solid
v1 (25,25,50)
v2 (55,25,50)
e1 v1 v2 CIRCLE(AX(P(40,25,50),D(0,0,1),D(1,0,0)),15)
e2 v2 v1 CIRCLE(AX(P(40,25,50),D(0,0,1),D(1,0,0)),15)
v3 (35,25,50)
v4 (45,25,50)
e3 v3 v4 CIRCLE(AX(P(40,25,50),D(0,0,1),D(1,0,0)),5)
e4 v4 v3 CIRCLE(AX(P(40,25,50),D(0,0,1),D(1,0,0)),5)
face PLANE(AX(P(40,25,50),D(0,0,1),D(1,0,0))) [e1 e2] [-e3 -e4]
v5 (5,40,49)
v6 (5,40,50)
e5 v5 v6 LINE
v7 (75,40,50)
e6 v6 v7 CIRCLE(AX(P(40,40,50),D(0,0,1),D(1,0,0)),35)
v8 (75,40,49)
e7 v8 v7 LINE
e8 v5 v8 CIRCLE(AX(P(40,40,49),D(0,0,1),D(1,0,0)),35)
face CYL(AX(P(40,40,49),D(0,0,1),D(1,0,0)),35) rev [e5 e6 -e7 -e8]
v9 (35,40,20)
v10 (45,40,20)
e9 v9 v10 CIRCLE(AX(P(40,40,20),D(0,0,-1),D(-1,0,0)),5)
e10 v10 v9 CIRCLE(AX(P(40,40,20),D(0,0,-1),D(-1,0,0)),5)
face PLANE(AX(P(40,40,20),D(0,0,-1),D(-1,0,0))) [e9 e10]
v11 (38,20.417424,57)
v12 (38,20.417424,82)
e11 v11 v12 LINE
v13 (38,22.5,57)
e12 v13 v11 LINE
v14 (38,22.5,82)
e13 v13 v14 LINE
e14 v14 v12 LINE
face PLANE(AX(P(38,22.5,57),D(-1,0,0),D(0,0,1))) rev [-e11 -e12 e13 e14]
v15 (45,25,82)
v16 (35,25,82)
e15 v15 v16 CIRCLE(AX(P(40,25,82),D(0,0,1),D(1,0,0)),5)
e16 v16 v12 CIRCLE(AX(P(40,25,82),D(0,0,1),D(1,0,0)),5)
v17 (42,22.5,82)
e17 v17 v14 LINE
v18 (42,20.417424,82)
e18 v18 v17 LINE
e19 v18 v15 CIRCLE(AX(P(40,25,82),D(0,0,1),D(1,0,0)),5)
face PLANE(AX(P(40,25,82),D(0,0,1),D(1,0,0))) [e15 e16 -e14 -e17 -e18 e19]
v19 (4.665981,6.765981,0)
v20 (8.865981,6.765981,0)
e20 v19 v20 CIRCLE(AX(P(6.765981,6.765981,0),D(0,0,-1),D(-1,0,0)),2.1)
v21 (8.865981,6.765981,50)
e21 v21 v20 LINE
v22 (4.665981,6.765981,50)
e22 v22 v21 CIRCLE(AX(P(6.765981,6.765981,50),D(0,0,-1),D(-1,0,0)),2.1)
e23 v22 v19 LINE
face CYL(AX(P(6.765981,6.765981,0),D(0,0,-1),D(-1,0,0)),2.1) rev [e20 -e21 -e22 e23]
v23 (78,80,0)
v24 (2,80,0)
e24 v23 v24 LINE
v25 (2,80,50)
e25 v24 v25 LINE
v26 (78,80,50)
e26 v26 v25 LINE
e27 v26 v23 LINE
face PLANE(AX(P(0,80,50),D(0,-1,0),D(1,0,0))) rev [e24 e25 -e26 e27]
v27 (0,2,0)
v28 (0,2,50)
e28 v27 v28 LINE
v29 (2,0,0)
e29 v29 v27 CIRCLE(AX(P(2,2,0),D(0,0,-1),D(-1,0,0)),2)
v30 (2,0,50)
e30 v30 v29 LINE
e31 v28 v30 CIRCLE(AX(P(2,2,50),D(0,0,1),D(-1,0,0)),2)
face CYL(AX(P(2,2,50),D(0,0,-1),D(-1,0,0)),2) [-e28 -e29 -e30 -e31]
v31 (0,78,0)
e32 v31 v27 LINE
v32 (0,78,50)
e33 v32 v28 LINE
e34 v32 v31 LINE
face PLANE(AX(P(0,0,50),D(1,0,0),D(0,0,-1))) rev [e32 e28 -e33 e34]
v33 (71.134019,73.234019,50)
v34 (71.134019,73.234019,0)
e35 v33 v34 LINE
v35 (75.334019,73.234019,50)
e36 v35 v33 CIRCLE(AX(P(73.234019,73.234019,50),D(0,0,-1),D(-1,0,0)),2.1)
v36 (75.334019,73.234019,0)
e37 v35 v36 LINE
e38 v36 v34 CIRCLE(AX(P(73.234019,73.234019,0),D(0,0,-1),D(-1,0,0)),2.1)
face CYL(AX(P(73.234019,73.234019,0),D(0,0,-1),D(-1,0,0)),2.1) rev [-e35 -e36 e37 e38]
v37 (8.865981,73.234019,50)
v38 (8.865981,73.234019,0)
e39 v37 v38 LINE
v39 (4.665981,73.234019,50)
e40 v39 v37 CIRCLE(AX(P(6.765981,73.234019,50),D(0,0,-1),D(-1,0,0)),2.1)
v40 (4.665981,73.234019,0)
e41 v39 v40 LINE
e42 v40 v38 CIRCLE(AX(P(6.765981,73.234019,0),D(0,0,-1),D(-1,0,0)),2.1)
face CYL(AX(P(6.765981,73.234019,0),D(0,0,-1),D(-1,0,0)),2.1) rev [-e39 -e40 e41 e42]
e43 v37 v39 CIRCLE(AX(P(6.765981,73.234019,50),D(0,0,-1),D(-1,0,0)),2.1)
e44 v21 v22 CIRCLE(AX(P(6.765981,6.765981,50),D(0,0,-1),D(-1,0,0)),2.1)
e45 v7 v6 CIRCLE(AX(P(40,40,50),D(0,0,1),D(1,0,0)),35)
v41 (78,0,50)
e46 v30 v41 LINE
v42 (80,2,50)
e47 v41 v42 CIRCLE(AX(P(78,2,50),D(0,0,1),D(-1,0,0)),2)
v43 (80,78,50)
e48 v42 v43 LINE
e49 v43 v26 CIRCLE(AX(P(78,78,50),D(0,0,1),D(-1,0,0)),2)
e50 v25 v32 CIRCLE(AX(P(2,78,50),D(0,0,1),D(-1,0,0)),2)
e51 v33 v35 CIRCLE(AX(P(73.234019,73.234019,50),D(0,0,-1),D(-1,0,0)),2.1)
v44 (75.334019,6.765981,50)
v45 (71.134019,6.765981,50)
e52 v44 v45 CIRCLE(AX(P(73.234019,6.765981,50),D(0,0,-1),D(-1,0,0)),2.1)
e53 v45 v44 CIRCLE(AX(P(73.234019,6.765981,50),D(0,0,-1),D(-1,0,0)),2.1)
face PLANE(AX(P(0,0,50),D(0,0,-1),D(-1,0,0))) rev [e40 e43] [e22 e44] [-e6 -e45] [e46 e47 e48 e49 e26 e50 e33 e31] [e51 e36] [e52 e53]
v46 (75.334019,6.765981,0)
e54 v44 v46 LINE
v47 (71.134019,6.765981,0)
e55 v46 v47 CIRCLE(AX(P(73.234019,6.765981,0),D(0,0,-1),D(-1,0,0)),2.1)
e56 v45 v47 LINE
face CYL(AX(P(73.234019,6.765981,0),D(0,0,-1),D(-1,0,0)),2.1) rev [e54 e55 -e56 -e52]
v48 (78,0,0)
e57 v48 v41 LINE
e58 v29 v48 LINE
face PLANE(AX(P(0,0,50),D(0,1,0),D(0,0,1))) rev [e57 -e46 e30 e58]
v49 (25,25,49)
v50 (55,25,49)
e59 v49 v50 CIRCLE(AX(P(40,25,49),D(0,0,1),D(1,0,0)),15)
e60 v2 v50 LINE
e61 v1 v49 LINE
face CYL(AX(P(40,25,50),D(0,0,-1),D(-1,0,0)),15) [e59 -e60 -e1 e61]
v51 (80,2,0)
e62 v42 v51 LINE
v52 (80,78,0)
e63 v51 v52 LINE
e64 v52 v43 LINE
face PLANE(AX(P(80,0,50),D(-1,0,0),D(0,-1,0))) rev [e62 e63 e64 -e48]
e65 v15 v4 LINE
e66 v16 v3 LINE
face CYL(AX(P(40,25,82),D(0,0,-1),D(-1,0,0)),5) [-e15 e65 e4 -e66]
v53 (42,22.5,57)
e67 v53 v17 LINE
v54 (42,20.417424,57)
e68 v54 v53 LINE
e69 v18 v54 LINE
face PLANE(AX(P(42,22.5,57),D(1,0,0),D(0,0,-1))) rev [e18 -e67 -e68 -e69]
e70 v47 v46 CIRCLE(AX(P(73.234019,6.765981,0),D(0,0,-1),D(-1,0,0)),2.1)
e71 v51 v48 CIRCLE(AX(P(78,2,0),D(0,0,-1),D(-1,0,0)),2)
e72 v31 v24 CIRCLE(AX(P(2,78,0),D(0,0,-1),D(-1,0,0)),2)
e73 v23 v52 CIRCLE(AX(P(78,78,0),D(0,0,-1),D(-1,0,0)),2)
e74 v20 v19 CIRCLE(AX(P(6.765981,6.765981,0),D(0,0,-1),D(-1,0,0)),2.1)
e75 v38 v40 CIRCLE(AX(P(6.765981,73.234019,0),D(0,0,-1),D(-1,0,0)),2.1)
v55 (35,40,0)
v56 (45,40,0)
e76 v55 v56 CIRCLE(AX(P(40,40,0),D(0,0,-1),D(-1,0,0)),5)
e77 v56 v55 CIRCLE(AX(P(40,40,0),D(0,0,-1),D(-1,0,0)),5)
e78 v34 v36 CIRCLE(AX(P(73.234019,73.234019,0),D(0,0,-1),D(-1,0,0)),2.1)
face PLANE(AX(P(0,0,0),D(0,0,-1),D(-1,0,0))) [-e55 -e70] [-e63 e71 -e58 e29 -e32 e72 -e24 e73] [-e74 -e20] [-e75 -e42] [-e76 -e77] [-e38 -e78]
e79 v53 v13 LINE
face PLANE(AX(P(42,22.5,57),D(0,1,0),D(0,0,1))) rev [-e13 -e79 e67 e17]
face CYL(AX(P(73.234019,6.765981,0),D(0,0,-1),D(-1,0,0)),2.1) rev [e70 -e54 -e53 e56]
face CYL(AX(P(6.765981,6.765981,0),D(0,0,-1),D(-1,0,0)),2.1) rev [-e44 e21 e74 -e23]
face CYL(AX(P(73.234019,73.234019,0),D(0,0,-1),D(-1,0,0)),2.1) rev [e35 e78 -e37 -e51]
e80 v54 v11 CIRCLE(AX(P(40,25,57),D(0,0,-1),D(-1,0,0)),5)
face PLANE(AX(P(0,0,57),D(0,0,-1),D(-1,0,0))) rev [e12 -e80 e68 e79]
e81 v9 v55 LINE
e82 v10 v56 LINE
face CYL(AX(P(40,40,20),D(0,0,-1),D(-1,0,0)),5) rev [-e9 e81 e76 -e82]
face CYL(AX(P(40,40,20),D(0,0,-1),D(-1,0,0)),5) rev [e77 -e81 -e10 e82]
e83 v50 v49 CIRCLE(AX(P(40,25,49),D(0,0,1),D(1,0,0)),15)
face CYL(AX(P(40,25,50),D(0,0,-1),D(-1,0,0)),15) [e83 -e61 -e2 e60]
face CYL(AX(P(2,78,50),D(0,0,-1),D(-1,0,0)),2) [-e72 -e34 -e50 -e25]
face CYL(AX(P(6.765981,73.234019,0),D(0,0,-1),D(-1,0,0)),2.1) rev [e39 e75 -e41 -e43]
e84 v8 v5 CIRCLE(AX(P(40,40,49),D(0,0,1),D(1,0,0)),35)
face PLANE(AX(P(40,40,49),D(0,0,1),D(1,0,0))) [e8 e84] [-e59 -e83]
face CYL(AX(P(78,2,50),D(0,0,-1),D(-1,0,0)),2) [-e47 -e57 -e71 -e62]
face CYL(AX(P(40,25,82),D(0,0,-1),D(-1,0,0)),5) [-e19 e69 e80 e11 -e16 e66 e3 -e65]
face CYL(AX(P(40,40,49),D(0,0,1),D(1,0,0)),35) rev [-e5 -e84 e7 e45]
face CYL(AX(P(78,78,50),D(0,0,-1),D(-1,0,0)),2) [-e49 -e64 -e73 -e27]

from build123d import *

# Parameters (mm, degrees)
SKETCH_1_W          = 80
SKETCH_1_H          = 80
EXTRUDE_1_DEPTH     = 50
SKETCH_2_R          = 35
CUT_EXTRUDE_1_DEPTH = 1
FILLET_1_R          = 2
HOLE_WIZARD_M5_1_D  = 4.2
SKETCH_10_R         = 5
CUT_EXTRUDE_2_DEPTH = 20
SKETCH_11_R         = 5
EXTRUDE_3_DEPTH     = 32
SKETCH_13_W         = 4
SKETCH_13_H         = 5
CUT_EXTRUDE_4_DEPTH = 25
SKETCH_14_R         = 15
EXTRUDE_4_DEPTH     = 1


with BuildPart() as part:
    # 草图1 → 凸台-拉伸1 (new body)
    with BuildSketch(Plane.XY):
        with Locations((40, 40)):
            Rectangle(SKETCH_1_W, SKETCH_1_H)
    extrude(amount=EXTRUDE_1_DEPTH)

    # 草图2 → 切除-拉伸1 (cut)
    with BuildSketch(Plane.XY.offset(50)):
        with Locations((40, 40)):
            Circle(SKETCH_2_R)
    extrude(amount=-CUT_EXTRUDE_1_DEPTH, mode=Mode.SUBTRACT)

    # 圆角1
    fillet_1_edges = [part.edges().sort_by_distance(p)[0] for p in [
        (0, 80, 25),
        (80, 80, 25),
        (80, 0, 25),
        (0, 0, 25),
    ]]
    fillet(fillet_1_edges, radius=FILLET_1_R)

    # M5 螺纹孔1 (through all)
    with Locations(Plane(origin=(73.234018716, 73.234018716, 0), x_dir=(-1, 0, 0), z_dir=(0, 0, -1))):
        with Locations((0, 0), (66.468037432, 0), (66.468037432, -66.468037432), (0, -66.468037432)):
            Hole(HOLE_WIZARD_M5_1_D / 2)

    # 草图10 → 切除-拉伸2 (cut)
    with BuildSketch(Plane(origin=(0, 0, 0), x_dir=(-1, 0, 0), z_dir=(0, 0, -1))):
        with Locations((-40, 40)):
            Circle(SKETCH_10_R)
    extrude(amount=-CUT_EXTRUDE_2_DEPTH, mode=Mode.SUBTRACT)



with BuildPart() as body_2:
    # 草图11 → 凸台-拉伸3 (new body)
    with BuildSketch(Plane.XY.offset(50)):
        with Locations((40, 25)):
            Circle(SKETCH_11_R)
    extrude(amount=EXTRUDE_3_DEPTH)

    # 草图13 → 切除-拉伸4 (cut)
    with BuildSketch(Plane.XY.offset(82)):
        with Locations((40, 20)):
            Rectangle(SKETCH_13_W, SKETCH_13_H)
    extrude(amount=-CUT_EXTRUDE_4_DEPTH, mode=Mode.SUBTRACT)


with BuildPart() as part_1:
    add(part.part)

    add(body_2.part)  # 凸台-拉伸4 merges body 2
    # 草图14 → 凸台-拉伸4 (add)
    with BuildSketch(Plane.XY.offset(49)):
        with Locations((40, 25)):
            Circle(SKETCH_14_R)
    extrude(amount=EXTRUDE_4_DEPTH)


solid = part_1.part
